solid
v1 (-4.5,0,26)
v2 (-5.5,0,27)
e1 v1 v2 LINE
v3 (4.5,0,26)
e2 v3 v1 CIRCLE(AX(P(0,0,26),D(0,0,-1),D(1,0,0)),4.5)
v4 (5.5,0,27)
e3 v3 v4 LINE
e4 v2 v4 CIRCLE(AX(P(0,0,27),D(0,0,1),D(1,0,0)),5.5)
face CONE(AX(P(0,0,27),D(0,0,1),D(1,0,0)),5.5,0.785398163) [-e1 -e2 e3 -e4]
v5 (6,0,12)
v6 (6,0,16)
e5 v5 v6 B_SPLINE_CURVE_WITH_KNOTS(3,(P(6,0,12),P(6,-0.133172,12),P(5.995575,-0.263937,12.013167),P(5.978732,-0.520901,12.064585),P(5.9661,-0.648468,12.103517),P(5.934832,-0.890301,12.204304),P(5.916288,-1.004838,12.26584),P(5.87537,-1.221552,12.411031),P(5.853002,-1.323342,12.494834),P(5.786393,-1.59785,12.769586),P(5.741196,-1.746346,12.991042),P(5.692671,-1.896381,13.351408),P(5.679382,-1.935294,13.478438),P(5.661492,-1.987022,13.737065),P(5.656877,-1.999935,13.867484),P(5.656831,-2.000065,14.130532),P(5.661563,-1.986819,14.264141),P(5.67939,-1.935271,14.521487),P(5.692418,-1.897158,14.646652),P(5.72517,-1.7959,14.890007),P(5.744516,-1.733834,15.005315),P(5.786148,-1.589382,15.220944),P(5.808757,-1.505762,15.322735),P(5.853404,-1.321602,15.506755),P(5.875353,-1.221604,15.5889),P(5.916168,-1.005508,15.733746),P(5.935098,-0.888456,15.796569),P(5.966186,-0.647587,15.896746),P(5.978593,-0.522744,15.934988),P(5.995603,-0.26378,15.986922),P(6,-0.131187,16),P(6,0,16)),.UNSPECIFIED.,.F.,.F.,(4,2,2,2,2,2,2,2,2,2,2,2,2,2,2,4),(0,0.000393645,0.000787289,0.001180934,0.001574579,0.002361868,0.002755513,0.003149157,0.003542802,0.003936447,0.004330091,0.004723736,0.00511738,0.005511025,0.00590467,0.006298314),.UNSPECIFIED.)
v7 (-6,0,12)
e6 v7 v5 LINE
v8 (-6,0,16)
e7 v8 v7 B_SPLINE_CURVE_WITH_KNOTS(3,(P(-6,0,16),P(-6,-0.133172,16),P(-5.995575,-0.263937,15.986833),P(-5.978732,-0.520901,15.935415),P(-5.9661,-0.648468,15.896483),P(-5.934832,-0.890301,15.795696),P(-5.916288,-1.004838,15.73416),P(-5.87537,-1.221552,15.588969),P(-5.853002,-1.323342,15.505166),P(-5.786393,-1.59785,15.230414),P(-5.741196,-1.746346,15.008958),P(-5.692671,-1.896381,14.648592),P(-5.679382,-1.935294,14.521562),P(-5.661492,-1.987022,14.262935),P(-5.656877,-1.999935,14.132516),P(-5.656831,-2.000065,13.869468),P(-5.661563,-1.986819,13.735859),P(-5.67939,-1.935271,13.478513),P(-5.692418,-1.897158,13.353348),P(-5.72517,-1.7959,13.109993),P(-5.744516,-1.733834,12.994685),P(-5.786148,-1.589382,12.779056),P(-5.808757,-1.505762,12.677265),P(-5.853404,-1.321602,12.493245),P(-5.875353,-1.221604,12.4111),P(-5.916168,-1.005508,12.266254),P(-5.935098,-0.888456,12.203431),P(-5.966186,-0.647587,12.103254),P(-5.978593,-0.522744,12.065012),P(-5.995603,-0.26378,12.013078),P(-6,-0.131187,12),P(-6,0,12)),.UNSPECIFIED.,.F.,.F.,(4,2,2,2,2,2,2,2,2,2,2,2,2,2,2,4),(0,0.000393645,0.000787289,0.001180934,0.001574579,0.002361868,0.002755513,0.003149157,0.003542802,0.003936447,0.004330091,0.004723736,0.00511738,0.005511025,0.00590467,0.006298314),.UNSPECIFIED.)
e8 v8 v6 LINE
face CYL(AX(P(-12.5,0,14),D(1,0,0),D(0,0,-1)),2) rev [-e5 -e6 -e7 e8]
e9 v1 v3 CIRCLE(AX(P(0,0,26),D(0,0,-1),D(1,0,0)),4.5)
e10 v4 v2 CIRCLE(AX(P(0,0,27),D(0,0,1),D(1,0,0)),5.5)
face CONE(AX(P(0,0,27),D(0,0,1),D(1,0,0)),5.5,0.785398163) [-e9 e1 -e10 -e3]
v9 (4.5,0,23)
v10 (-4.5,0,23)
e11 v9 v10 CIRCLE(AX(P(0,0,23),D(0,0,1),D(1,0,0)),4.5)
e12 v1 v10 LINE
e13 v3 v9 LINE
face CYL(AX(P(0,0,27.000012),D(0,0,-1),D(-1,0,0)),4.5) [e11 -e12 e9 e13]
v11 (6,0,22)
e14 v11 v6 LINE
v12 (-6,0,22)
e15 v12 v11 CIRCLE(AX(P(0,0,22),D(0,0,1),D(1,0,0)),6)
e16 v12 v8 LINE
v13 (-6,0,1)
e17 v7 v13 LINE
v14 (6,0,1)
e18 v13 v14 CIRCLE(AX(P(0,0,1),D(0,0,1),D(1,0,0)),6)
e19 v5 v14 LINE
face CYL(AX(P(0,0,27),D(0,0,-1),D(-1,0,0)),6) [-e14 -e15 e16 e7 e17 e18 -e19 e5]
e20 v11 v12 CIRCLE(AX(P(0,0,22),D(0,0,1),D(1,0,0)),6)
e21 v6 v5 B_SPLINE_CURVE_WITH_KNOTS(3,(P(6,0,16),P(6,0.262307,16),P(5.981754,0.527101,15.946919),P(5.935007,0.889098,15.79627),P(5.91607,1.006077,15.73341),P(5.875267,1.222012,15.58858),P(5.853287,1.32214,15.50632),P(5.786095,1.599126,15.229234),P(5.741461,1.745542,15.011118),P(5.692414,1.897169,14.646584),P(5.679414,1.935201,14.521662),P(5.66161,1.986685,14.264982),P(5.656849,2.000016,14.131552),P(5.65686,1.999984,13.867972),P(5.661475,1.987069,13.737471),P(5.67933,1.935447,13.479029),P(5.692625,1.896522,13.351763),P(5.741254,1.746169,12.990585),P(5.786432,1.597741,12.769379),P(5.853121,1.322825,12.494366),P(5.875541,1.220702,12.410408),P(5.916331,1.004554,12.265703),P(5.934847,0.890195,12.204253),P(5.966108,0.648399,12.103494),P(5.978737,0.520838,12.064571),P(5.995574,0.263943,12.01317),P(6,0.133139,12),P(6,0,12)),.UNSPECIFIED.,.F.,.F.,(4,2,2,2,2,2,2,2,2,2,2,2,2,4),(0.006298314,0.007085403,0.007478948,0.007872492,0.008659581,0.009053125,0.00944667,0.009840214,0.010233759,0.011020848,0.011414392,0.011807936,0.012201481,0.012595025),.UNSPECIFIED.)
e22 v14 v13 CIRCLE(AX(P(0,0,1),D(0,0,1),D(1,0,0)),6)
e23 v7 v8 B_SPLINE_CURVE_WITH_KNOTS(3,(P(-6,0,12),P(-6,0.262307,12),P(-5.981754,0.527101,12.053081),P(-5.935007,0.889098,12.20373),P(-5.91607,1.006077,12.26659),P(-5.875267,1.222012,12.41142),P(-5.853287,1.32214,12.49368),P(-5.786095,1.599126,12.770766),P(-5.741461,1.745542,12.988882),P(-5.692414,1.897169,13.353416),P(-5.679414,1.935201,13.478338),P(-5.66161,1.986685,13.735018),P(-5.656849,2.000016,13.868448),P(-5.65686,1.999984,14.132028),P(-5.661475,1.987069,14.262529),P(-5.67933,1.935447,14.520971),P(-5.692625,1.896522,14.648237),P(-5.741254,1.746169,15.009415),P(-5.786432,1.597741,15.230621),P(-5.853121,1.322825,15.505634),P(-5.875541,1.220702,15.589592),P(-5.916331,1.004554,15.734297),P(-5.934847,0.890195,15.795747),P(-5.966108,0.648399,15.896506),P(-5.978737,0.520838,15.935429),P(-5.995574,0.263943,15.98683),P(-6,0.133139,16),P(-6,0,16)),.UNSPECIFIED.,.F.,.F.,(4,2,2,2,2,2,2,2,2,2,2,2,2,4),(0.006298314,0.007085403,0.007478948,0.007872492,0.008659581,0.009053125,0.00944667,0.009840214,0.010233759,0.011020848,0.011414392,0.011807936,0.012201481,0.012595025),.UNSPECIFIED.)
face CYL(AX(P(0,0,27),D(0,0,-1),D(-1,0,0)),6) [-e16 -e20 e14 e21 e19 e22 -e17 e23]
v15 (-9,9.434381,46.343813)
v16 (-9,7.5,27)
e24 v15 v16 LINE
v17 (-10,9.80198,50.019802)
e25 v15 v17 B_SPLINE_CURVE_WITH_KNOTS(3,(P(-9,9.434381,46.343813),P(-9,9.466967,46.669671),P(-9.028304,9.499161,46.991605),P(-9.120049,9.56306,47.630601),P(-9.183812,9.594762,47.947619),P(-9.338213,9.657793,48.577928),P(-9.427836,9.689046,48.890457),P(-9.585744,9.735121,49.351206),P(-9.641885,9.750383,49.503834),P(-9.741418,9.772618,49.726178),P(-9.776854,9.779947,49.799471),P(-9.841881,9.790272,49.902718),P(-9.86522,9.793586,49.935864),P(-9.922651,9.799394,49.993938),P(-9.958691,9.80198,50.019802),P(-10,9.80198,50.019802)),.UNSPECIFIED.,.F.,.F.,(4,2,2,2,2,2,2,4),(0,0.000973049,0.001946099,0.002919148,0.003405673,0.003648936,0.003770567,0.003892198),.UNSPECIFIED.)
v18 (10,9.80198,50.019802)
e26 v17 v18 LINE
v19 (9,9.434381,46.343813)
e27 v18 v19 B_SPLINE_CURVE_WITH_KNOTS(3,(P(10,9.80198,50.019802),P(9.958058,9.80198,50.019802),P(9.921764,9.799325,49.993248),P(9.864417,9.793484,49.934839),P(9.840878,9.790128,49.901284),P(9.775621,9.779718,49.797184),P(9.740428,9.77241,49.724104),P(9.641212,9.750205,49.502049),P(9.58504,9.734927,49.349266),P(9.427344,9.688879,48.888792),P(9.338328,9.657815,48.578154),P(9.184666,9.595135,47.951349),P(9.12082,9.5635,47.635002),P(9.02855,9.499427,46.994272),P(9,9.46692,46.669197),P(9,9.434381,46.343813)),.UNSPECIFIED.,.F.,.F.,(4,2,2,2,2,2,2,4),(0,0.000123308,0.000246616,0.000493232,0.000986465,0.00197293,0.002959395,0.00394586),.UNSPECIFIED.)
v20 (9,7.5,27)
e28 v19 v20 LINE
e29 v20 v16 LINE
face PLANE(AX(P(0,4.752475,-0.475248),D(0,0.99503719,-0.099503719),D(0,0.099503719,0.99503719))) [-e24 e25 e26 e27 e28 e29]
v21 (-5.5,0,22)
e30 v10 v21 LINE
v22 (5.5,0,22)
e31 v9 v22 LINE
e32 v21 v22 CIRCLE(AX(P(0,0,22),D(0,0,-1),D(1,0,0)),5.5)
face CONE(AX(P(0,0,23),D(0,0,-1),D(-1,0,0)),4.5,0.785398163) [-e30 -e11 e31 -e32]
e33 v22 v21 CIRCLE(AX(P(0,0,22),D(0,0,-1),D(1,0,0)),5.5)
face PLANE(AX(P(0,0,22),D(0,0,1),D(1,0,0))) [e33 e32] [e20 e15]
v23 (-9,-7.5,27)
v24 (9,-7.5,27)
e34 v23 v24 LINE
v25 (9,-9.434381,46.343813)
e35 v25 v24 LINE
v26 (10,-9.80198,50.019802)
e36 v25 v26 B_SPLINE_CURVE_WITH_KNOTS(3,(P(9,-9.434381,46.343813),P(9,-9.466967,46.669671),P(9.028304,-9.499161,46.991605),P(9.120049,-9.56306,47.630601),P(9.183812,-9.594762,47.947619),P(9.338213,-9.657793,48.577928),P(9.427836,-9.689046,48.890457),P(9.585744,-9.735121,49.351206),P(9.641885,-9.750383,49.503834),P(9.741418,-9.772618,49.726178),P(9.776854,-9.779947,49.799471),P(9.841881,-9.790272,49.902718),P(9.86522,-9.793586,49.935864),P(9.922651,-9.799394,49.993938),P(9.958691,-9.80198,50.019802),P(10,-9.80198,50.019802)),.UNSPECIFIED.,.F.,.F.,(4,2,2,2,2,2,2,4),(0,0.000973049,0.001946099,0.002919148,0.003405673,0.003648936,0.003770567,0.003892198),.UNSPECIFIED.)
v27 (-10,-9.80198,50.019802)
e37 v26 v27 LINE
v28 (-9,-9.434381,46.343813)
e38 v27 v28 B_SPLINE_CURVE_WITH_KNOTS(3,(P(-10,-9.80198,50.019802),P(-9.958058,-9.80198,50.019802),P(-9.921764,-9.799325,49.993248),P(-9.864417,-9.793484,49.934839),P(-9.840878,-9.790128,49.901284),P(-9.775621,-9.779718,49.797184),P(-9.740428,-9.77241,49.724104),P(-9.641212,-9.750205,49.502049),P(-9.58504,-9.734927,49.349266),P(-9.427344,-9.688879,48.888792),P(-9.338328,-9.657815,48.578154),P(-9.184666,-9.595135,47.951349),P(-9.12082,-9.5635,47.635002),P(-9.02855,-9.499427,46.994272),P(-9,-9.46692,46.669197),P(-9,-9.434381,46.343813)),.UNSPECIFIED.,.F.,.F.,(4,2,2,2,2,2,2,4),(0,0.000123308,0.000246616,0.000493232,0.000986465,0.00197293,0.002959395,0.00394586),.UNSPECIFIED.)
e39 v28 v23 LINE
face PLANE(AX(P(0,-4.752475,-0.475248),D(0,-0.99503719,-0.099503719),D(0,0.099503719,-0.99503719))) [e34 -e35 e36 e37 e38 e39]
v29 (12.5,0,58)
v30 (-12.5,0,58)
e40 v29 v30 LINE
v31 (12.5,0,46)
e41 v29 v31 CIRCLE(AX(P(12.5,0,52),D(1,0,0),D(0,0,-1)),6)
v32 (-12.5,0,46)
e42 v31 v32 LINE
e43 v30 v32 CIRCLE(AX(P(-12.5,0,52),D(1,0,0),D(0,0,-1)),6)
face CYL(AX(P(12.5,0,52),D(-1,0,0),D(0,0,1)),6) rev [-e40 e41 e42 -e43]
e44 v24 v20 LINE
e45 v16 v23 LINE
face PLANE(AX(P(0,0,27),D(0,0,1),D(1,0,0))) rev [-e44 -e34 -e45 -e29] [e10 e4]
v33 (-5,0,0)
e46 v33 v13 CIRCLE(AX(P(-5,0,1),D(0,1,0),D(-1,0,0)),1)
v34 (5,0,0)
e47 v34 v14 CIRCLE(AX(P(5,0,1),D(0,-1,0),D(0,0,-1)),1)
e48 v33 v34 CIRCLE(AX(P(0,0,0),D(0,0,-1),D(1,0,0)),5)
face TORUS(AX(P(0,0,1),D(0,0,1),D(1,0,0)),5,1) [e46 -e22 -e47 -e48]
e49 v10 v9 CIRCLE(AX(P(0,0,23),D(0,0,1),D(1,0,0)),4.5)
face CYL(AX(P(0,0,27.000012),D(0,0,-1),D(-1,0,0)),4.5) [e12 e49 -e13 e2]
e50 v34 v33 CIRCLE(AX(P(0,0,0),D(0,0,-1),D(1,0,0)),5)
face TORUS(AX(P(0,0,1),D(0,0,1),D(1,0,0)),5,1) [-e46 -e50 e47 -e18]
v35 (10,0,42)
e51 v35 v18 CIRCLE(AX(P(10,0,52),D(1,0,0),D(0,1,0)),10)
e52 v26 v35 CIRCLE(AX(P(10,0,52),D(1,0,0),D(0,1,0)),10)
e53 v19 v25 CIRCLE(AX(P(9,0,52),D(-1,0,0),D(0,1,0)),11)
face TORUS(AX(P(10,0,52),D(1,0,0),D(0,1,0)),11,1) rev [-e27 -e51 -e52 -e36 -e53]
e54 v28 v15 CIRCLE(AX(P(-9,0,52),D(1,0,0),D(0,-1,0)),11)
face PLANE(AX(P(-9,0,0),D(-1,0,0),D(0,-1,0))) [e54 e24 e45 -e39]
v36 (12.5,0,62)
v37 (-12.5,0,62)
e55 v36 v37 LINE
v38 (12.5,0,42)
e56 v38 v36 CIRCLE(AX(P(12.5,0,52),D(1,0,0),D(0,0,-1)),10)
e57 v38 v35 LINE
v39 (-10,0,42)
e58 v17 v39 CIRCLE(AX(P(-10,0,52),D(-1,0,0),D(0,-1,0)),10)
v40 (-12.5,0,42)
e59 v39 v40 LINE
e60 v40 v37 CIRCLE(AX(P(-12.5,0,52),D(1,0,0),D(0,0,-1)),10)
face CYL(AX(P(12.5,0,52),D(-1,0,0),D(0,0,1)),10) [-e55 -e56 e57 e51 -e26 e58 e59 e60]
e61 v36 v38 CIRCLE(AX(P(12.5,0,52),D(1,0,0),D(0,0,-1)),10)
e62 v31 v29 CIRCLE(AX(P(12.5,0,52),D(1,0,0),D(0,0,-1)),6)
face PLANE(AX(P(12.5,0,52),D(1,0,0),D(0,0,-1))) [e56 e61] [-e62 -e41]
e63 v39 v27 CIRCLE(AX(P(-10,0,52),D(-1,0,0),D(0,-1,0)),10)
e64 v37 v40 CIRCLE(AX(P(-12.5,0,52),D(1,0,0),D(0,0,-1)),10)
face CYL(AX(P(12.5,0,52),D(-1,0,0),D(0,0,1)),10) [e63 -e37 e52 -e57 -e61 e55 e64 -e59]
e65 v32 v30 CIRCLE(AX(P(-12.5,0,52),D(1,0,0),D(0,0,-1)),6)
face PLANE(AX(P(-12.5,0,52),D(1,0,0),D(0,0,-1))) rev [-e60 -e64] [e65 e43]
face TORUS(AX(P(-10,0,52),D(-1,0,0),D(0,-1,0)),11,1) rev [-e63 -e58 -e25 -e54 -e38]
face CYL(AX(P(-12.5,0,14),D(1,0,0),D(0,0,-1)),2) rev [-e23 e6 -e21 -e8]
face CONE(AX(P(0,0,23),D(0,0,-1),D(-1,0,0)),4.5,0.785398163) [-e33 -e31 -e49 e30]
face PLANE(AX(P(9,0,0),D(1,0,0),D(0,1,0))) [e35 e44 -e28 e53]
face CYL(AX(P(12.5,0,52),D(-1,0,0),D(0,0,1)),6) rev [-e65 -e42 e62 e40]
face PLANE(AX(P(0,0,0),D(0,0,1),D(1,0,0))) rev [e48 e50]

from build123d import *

# Parameters (mm, degrees)
SHANK_PROFILE_12_R           = 6
SHANK_12X27_DEPTH            = 27
SHANK_STEP_9X5_DEPTH         = 29.301943396
SHANK_STEP_9X5_DEPTH_BACK    = 5
SHANK_STEP_PROFILE_9_R       = 6
SHANK_STEP_PROFILE_9_R_2     = 4.5
EYE_PROFILE_20_R             = 10
EYE_PROFILE_20_R_2           = 6
EYE_BOSS_20X25_DEPTH         = 12.5
EYE_START                    = -35
EYE_BORE_PROFILE_R           = 6
EYE_BORE_DEPTH               = 35
CROSS_HOLE_4_DEPTH           = 65.033194649
CROSS_HOLE_4_DEPTH_BACK      = 65.033194649
CROSS_HOLE_PROFILE_4_R       = 2
EYE_BLEND_FILLET_R1_R        = 1
SHANK_STEP_CHAMFER_1X45_SIZE = 1


with BuildPart() as part:
    # Shank Profile Ø12 → Shank Ø12x27 (new body)
    with BuildSketch(Plane.XY):
        Circle(SHANK_PROFILE_12_R)
    extrude(amount=SHANK_12X27_DEPTH)

    # Shank Step Profile Ø9 → Shank Step Ø9x5 (cut, two sides: drawn at the far end of the back side and taken through both)
    with BuildSketch(Plane.XY.offset(27).offset(-SHANK_STEP_9X5_DEPTH_BACK)):
        Circle(SHANK_STEP_PROFILE_9_R)
        Circle(SHANK_STEP_PROFILE_9_R_2, mode=Mode.SUBTRACT)
    extrude(amount=SHANK_STEP_9X5_DEPTH + SHANK_STEP_9X5_DEPTH_BACK, mode=Mode.SUBTRACT)



with BuildPart() as body_2:
    # Eye Profile Ø20 → Eye Boss Ø20x25 (new, symmetric)
    with BuildSketch(Plane(origin=(0, 0, 0), x_dir=(0, 0, -1), z_dir=(1, 0, 0))):
        with Locations((-52, 0)):
            Circle(EYE_PROFILE_20_R)
        with Locations((-52, 0)):
            Circle(EYE_PROFILE_20_R_2, mode=Mode.SUBTRACT)
    extrude(amount=EYE_BOSS_20X25_DEPTH, both=True)


with BuildPart() as part_1:
    add(part.part)

    add(body_2.part)  # Shank To Eye Transition merges body 2
    # Loft End Section 18x20 → Shank To Eye Transition section 0
    with BuildSketch(Plane.XY.offset(52)):
        with BuildLine():
            Line((-9, 10), (9, 10))
            Line((9, 10), (9, -10))
            Line((9, -10), (-9, -10))
            Line((-9, -10), (-9, 10))
        make_face()
    # Loft Start Section 18x15 → Shank To Eye Transition section 1
    with BuildSketch(Plane.XY.offset(27)):
        with BuildLine():
            Line((-9, 7.5), (9, 7.5))
            Line((9, 7.5), (9, -7.5))
            Line((9, -7.5), (-9, -7.5))
            Line((-9, -7.5), (-9, 7.5))
        make_face()
    loft()

    # Eye Bore Profile → Eye Bore (cut)
    with BuildSketch(Plane(origin=(12.5, 0, 0), x_dir=(0, 0, -1), z_dir=(1, 0, 0)).offset(EYE_START)):
        with Locations((-52, 0)):
            Circle(EYE_BORE_PROFILE_R)
    extrude(amount=EYE_BORE_DEPTH, mode=Mode.SUBTRACT)

    # Cross Hole Profile Ø4 → Cross Hole Ø4 (cut, two sides: drawn at the far end of the back side and taken through both)
    with BuildSketch(Plane(origin=(0, 0, 0), x_dir=(0, 0, -1), z_dir=(1, 0, 0)).offset(-CROSS_HOLE_4_DEPTH_BACK)):
        with Locations(Location((-14, 0, 0), (0, 0, 180))):
            Circle(CROSS_HOLE_PROFILE_4_R)
    extrude(amount=CROSS_HOLE_4_DEPTH + CROSS_HOLE_4_DEPTH_BACK, mode=Mode.SUBTRACT)

    # Eye Blend Fillet R1
    eye_blend_fillet_r1_edges = [part_1.edges().sort_by_distance(p)[0] for p in [
        (-9, -6.332377898, 44.260427013),
        (9, 6.332377898, 44.260427013),
        (-6, 0, 0),
    ]]
    fillet(eye_blend_fillet_r1_edges, radius=EYE_BLEND_FILLET_R1_R)

    # Shank Step Chamfer 1x45
    shank_step_chamfer_1x45_edges = [part_1.edges().sort_by_distance(p)[0] for p in [
        (-4.5, 0, 27),
        (-4.5, 0, 22),
    ]]
    chamfer(shank_step_chamfer_1x45_edges, length=SHANK_STEP_CHAMFER_1X45_SIZE)


solid = part_1.part
